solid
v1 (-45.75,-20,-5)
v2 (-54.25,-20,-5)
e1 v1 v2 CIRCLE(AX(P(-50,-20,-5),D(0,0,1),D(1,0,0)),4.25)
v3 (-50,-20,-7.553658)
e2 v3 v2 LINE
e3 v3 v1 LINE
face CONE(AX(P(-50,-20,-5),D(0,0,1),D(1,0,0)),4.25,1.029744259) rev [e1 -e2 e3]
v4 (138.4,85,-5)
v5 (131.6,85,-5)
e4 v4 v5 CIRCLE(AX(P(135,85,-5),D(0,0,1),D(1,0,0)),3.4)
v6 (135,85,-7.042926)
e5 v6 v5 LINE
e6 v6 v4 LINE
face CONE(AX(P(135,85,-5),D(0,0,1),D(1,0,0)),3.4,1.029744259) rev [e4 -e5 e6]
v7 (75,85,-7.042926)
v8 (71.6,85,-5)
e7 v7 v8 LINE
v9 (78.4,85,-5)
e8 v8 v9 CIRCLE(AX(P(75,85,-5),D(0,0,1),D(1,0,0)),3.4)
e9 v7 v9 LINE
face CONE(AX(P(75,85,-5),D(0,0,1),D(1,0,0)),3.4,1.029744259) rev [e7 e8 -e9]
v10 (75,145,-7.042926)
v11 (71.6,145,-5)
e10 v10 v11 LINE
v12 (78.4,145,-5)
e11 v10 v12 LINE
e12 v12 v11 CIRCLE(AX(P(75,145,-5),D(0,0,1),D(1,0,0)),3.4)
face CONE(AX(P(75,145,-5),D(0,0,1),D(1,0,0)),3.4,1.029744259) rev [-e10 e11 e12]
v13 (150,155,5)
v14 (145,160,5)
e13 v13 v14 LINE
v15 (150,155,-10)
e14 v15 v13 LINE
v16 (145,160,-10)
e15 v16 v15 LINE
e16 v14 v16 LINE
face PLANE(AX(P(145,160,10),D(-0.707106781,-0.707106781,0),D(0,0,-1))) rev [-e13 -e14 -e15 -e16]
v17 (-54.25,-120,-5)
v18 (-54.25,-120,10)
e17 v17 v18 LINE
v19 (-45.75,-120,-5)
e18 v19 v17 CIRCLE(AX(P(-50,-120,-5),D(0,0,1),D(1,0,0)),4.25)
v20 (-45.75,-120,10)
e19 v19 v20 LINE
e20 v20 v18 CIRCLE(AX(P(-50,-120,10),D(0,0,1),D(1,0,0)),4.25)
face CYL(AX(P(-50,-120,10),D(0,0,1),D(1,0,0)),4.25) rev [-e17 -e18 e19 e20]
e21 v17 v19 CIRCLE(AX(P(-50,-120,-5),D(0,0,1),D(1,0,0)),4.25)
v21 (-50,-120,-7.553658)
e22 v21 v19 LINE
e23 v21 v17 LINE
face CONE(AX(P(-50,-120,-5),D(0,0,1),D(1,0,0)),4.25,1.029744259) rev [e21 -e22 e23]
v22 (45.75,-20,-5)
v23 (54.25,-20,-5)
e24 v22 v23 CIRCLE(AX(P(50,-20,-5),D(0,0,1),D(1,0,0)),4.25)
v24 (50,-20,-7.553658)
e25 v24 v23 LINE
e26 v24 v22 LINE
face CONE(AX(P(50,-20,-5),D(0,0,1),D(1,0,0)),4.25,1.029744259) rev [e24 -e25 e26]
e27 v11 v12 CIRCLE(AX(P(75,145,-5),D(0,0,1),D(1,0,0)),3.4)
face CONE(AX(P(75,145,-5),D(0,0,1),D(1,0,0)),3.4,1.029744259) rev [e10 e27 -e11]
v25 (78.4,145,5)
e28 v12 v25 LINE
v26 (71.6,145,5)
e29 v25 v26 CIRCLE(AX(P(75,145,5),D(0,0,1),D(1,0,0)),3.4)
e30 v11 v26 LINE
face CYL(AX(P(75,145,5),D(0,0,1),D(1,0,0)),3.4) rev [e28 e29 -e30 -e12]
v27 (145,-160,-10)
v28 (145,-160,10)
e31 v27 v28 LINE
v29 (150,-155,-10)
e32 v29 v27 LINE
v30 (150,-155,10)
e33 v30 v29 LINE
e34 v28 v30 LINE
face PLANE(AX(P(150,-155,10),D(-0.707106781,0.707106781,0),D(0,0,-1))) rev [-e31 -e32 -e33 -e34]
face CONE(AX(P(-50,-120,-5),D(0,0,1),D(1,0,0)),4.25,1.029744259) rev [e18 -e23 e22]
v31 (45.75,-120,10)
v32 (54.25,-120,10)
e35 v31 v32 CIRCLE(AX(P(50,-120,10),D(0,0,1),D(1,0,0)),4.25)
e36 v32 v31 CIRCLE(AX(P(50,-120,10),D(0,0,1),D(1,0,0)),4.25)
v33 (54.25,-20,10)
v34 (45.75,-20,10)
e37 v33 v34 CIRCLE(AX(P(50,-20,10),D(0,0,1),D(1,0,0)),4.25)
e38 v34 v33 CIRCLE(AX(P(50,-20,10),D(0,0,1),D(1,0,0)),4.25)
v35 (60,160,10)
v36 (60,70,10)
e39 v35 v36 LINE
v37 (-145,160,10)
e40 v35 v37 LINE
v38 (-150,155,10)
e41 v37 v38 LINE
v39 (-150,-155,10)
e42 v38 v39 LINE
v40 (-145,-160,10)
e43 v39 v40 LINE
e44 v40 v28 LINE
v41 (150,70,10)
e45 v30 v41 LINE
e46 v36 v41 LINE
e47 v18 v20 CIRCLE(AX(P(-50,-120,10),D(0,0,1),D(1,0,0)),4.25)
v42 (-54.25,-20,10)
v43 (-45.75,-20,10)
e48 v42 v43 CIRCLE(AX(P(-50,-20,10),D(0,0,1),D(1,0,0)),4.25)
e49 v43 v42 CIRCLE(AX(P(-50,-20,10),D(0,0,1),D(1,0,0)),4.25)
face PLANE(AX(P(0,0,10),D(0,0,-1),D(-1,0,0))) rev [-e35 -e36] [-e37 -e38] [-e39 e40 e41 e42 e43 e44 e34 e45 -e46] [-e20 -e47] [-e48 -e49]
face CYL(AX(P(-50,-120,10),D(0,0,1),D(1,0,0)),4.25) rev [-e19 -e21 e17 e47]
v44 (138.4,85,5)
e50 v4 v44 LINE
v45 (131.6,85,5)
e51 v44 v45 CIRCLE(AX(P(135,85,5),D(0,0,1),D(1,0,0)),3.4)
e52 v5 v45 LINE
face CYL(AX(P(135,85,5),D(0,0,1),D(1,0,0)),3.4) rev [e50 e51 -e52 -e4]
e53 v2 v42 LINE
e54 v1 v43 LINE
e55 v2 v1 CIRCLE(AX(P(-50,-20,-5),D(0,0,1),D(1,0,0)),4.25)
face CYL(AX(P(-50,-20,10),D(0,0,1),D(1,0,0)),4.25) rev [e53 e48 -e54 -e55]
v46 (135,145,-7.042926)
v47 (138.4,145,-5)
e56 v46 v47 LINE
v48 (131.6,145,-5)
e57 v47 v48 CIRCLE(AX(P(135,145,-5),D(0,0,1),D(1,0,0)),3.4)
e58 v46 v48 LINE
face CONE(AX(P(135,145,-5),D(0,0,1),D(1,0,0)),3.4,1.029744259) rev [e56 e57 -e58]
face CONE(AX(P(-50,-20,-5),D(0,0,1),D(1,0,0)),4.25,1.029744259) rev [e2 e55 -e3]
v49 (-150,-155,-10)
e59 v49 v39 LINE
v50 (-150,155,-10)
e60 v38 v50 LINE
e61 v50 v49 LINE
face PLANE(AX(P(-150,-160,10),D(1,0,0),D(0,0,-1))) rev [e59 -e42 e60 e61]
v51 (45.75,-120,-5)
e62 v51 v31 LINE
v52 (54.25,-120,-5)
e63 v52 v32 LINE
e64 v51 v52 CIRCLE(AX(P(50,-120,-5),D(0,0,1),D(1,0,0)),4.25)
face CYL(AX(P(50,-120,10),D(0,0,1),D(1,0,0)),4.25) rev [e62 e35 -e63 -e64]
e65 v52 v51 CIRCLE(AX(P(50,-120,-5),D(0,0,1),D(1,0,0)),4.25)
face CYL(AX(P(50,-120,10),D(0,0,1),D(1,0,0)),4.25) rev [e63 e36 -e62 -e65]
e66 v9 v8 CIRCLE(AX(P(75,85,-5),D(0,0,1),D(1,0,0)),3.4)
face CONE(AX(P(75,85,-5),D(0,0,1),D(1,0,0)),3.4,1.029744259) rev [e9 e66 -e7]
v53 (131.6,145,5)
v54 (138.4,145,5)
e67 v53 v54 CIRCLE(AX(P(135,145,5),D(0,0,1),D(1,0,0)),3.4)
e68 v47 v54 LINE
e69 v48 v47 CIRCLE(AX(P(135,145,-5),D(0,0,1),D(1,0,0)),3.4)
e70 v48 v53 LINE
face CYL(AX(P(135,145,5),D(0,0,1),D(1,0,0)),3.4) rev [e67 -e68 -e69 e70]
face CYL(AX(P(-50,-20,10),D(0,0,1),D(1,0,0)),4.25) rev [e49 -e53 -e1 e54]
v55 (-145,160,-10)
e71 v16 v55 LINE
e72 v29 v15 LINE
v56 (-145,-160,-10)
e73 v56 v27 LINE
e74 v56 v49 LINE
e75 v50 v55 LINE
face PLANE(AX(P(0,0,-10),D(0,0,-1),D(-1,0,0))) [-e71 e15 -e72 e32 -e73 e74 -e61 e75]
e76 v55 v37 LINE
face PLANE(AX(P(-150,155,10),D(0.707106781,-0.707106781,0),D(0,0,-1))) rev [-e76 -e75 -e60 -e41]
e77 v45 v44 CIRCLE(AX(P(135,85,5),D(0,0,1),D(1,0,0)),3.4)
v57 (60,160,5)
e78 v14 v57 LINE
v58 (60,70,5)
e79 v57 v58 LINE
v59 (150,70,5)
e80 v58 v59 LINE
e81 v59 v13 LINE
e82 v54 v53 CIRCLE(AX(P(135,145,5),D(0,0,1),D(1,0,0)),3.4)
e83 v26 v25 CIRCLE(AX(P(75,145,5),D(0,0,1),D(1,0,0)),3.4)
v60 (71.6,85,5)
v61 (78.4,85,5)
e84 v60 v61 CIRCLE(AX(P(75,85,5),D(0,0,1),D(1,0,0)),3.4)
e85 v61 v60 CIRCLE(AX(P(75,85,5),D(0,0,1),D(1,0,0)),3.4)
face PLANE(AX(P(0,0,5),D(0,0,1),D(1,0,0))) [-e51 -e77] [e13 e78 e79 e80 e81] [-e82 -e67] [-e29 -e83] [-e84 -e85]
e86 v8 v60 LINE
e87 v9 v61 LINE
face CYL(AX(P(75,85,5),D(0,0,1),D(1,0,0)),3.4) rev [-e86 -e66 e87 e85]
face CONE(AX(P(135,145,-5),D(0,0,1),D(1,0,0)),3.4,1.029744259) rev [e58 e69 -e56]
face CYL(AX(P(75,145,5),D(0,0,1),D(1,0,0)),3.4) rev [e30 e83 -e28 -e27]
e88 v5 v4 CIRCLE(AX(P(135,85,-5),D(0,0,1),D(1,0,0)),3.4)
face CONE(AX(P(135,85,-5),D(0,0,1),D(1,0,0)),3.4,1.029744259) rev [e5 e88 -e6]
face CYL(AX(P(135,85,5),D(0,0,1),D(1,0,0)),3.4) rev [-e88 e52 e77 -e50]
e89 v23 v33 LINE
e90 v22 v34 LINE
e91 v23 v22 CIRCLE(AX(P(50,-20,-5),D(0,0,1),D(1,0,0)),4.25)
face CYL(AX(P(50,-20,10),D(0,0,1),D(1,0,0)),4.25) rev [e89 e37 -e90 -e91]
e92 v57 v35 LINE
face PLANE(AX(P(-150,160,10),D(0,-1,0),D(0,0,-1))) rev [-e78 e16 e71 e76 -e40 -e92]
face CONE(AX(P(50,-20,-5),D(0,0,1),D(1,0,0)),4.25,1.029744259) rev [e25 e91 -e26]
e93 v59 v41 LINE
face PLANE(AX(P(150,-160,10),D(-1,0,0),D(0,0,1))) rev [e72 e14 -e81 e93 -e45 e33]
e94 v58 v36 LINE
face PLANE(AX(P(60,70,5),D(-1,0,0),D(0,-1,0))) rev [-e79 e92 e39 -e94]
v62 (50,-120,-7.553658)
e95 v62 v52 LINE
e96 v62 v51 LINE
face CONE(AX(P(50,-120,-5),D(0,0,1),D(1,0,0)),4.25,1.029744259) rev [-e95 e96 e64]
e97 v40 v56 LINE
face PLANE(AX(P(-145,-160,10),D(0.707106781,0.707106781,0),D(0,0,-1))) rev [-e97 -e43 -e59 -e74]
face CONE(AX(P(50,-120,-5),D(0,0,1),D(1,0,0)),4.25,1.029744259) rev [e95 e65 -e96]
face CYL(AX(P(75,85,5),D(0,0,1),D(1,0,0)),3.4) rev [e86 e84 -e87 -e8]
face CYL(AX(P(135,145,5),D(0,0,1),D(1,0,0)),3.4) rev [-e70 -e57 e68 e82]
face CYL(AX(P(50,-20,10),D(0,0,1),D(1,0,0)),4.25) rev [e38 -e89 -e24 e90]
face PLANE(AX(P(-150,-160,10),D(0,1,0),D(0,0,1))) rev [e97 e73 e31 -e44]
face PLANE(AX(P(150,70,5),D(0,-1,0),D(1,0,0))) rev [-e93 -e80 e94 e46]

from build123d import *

# Parameters (mm, degrees)
SKETCH_1_W              = 300
SKETCH_1_H              = 320
EXTRUDE_1_DEPTH         = 10
HOLE_WIZARD_M10_1_D     = 8.5
HOLE_WIZARD_M10_1_DEPTH = 15
HOLE_WIZARD_M10_1_TIP   = 2.553657631
SKETCH_7_W              = 90
SKETCH_7_H              = 90
CUT_EXTRUDE_1_DEPTH     = 5
HOLE_WIZARD_M8_1_D      = 6.8
HOLE_WIZARD_M8_1_DEPTH  = 10
HOLE_WIZARD_M8_1_TIP    = 2.042926105
CHAMFER_1_SIZE          = 5


with BuildPart() as part:
    # 草图1 → 凸台-拉伸1 (new, symmetric)
    with BuildSketch(Plane.XY):
        Rectangle(SKETCH_1_W, SKETCH_1_H)
    extrude(amount=EXTRUDE_1_DEPTH, both=True)

    # M10 螺纹孔1
    with Locations(Plane.XY.offset(10)):
        with Locations((50, -20), (-50, -120), (-50, -20), (50, -120)):
            Hole(HOLE_WIZARD_M10_1_D / 2, depth=HOLE_WIZARD_M10_1_DEPTH)
            with Locations((0, 0, -(HOLE_WIZARD_M10_1_DEPTH + HOLE_WIZARD_M10_1_TIP / 2))):  # 118° drill point
                Cone(0, HOLE_WIZARD_M10_1_D / 2, HOLE_WIZARD_M10_1_TIP, mode=Mode.SUBTRACT)

    # 草图7 → 切除-拉伸1 (cut)
    with BuildSketch(Plane.XY.offset(10)):
        with Locations((105, 115)):
            Rectangle(SKETCH_7_W, SKETCH_7_H)
    extrude(amount=-CUT_EXTRUDE_1_DEPTH, mode=Mode.SUBTRACT)

    # M8 螺纹孔1
    with Locations(Plane.XY.offset(5)):
        with Locations((135, 145), (75, 85), (75, 145), (135, 85)):
            Hole(HOLE_WIZARD_M8_1_D / 2, depth=HOLE_WIZARD_M8_1_DEPTH)
            with Locations((0, 0, -(HOLE_WIZARD_M8_1_DEPTH + HOLE_WIZARD_M8_1_TIP / 2))):  # 118° drill point
                Cone(0, HOLE_WIZARD_M8_1_D / 2, HOLE_WIZARD_M8_1_TIP, mode=Mode.SUBTRACT)

    # 倒角1
    chamfer_1_edges = [part.edges().sort_by_distance(p)[0] for p in [
        (150, 160, -2.5),
        (150, -160, 0),
        (-150, -160, 0),
        (-150, 160, 0),
    ]]
    chamfer(chamfer_1_edges, length=CHAMFER_1_SIZE)


solid = part.part
